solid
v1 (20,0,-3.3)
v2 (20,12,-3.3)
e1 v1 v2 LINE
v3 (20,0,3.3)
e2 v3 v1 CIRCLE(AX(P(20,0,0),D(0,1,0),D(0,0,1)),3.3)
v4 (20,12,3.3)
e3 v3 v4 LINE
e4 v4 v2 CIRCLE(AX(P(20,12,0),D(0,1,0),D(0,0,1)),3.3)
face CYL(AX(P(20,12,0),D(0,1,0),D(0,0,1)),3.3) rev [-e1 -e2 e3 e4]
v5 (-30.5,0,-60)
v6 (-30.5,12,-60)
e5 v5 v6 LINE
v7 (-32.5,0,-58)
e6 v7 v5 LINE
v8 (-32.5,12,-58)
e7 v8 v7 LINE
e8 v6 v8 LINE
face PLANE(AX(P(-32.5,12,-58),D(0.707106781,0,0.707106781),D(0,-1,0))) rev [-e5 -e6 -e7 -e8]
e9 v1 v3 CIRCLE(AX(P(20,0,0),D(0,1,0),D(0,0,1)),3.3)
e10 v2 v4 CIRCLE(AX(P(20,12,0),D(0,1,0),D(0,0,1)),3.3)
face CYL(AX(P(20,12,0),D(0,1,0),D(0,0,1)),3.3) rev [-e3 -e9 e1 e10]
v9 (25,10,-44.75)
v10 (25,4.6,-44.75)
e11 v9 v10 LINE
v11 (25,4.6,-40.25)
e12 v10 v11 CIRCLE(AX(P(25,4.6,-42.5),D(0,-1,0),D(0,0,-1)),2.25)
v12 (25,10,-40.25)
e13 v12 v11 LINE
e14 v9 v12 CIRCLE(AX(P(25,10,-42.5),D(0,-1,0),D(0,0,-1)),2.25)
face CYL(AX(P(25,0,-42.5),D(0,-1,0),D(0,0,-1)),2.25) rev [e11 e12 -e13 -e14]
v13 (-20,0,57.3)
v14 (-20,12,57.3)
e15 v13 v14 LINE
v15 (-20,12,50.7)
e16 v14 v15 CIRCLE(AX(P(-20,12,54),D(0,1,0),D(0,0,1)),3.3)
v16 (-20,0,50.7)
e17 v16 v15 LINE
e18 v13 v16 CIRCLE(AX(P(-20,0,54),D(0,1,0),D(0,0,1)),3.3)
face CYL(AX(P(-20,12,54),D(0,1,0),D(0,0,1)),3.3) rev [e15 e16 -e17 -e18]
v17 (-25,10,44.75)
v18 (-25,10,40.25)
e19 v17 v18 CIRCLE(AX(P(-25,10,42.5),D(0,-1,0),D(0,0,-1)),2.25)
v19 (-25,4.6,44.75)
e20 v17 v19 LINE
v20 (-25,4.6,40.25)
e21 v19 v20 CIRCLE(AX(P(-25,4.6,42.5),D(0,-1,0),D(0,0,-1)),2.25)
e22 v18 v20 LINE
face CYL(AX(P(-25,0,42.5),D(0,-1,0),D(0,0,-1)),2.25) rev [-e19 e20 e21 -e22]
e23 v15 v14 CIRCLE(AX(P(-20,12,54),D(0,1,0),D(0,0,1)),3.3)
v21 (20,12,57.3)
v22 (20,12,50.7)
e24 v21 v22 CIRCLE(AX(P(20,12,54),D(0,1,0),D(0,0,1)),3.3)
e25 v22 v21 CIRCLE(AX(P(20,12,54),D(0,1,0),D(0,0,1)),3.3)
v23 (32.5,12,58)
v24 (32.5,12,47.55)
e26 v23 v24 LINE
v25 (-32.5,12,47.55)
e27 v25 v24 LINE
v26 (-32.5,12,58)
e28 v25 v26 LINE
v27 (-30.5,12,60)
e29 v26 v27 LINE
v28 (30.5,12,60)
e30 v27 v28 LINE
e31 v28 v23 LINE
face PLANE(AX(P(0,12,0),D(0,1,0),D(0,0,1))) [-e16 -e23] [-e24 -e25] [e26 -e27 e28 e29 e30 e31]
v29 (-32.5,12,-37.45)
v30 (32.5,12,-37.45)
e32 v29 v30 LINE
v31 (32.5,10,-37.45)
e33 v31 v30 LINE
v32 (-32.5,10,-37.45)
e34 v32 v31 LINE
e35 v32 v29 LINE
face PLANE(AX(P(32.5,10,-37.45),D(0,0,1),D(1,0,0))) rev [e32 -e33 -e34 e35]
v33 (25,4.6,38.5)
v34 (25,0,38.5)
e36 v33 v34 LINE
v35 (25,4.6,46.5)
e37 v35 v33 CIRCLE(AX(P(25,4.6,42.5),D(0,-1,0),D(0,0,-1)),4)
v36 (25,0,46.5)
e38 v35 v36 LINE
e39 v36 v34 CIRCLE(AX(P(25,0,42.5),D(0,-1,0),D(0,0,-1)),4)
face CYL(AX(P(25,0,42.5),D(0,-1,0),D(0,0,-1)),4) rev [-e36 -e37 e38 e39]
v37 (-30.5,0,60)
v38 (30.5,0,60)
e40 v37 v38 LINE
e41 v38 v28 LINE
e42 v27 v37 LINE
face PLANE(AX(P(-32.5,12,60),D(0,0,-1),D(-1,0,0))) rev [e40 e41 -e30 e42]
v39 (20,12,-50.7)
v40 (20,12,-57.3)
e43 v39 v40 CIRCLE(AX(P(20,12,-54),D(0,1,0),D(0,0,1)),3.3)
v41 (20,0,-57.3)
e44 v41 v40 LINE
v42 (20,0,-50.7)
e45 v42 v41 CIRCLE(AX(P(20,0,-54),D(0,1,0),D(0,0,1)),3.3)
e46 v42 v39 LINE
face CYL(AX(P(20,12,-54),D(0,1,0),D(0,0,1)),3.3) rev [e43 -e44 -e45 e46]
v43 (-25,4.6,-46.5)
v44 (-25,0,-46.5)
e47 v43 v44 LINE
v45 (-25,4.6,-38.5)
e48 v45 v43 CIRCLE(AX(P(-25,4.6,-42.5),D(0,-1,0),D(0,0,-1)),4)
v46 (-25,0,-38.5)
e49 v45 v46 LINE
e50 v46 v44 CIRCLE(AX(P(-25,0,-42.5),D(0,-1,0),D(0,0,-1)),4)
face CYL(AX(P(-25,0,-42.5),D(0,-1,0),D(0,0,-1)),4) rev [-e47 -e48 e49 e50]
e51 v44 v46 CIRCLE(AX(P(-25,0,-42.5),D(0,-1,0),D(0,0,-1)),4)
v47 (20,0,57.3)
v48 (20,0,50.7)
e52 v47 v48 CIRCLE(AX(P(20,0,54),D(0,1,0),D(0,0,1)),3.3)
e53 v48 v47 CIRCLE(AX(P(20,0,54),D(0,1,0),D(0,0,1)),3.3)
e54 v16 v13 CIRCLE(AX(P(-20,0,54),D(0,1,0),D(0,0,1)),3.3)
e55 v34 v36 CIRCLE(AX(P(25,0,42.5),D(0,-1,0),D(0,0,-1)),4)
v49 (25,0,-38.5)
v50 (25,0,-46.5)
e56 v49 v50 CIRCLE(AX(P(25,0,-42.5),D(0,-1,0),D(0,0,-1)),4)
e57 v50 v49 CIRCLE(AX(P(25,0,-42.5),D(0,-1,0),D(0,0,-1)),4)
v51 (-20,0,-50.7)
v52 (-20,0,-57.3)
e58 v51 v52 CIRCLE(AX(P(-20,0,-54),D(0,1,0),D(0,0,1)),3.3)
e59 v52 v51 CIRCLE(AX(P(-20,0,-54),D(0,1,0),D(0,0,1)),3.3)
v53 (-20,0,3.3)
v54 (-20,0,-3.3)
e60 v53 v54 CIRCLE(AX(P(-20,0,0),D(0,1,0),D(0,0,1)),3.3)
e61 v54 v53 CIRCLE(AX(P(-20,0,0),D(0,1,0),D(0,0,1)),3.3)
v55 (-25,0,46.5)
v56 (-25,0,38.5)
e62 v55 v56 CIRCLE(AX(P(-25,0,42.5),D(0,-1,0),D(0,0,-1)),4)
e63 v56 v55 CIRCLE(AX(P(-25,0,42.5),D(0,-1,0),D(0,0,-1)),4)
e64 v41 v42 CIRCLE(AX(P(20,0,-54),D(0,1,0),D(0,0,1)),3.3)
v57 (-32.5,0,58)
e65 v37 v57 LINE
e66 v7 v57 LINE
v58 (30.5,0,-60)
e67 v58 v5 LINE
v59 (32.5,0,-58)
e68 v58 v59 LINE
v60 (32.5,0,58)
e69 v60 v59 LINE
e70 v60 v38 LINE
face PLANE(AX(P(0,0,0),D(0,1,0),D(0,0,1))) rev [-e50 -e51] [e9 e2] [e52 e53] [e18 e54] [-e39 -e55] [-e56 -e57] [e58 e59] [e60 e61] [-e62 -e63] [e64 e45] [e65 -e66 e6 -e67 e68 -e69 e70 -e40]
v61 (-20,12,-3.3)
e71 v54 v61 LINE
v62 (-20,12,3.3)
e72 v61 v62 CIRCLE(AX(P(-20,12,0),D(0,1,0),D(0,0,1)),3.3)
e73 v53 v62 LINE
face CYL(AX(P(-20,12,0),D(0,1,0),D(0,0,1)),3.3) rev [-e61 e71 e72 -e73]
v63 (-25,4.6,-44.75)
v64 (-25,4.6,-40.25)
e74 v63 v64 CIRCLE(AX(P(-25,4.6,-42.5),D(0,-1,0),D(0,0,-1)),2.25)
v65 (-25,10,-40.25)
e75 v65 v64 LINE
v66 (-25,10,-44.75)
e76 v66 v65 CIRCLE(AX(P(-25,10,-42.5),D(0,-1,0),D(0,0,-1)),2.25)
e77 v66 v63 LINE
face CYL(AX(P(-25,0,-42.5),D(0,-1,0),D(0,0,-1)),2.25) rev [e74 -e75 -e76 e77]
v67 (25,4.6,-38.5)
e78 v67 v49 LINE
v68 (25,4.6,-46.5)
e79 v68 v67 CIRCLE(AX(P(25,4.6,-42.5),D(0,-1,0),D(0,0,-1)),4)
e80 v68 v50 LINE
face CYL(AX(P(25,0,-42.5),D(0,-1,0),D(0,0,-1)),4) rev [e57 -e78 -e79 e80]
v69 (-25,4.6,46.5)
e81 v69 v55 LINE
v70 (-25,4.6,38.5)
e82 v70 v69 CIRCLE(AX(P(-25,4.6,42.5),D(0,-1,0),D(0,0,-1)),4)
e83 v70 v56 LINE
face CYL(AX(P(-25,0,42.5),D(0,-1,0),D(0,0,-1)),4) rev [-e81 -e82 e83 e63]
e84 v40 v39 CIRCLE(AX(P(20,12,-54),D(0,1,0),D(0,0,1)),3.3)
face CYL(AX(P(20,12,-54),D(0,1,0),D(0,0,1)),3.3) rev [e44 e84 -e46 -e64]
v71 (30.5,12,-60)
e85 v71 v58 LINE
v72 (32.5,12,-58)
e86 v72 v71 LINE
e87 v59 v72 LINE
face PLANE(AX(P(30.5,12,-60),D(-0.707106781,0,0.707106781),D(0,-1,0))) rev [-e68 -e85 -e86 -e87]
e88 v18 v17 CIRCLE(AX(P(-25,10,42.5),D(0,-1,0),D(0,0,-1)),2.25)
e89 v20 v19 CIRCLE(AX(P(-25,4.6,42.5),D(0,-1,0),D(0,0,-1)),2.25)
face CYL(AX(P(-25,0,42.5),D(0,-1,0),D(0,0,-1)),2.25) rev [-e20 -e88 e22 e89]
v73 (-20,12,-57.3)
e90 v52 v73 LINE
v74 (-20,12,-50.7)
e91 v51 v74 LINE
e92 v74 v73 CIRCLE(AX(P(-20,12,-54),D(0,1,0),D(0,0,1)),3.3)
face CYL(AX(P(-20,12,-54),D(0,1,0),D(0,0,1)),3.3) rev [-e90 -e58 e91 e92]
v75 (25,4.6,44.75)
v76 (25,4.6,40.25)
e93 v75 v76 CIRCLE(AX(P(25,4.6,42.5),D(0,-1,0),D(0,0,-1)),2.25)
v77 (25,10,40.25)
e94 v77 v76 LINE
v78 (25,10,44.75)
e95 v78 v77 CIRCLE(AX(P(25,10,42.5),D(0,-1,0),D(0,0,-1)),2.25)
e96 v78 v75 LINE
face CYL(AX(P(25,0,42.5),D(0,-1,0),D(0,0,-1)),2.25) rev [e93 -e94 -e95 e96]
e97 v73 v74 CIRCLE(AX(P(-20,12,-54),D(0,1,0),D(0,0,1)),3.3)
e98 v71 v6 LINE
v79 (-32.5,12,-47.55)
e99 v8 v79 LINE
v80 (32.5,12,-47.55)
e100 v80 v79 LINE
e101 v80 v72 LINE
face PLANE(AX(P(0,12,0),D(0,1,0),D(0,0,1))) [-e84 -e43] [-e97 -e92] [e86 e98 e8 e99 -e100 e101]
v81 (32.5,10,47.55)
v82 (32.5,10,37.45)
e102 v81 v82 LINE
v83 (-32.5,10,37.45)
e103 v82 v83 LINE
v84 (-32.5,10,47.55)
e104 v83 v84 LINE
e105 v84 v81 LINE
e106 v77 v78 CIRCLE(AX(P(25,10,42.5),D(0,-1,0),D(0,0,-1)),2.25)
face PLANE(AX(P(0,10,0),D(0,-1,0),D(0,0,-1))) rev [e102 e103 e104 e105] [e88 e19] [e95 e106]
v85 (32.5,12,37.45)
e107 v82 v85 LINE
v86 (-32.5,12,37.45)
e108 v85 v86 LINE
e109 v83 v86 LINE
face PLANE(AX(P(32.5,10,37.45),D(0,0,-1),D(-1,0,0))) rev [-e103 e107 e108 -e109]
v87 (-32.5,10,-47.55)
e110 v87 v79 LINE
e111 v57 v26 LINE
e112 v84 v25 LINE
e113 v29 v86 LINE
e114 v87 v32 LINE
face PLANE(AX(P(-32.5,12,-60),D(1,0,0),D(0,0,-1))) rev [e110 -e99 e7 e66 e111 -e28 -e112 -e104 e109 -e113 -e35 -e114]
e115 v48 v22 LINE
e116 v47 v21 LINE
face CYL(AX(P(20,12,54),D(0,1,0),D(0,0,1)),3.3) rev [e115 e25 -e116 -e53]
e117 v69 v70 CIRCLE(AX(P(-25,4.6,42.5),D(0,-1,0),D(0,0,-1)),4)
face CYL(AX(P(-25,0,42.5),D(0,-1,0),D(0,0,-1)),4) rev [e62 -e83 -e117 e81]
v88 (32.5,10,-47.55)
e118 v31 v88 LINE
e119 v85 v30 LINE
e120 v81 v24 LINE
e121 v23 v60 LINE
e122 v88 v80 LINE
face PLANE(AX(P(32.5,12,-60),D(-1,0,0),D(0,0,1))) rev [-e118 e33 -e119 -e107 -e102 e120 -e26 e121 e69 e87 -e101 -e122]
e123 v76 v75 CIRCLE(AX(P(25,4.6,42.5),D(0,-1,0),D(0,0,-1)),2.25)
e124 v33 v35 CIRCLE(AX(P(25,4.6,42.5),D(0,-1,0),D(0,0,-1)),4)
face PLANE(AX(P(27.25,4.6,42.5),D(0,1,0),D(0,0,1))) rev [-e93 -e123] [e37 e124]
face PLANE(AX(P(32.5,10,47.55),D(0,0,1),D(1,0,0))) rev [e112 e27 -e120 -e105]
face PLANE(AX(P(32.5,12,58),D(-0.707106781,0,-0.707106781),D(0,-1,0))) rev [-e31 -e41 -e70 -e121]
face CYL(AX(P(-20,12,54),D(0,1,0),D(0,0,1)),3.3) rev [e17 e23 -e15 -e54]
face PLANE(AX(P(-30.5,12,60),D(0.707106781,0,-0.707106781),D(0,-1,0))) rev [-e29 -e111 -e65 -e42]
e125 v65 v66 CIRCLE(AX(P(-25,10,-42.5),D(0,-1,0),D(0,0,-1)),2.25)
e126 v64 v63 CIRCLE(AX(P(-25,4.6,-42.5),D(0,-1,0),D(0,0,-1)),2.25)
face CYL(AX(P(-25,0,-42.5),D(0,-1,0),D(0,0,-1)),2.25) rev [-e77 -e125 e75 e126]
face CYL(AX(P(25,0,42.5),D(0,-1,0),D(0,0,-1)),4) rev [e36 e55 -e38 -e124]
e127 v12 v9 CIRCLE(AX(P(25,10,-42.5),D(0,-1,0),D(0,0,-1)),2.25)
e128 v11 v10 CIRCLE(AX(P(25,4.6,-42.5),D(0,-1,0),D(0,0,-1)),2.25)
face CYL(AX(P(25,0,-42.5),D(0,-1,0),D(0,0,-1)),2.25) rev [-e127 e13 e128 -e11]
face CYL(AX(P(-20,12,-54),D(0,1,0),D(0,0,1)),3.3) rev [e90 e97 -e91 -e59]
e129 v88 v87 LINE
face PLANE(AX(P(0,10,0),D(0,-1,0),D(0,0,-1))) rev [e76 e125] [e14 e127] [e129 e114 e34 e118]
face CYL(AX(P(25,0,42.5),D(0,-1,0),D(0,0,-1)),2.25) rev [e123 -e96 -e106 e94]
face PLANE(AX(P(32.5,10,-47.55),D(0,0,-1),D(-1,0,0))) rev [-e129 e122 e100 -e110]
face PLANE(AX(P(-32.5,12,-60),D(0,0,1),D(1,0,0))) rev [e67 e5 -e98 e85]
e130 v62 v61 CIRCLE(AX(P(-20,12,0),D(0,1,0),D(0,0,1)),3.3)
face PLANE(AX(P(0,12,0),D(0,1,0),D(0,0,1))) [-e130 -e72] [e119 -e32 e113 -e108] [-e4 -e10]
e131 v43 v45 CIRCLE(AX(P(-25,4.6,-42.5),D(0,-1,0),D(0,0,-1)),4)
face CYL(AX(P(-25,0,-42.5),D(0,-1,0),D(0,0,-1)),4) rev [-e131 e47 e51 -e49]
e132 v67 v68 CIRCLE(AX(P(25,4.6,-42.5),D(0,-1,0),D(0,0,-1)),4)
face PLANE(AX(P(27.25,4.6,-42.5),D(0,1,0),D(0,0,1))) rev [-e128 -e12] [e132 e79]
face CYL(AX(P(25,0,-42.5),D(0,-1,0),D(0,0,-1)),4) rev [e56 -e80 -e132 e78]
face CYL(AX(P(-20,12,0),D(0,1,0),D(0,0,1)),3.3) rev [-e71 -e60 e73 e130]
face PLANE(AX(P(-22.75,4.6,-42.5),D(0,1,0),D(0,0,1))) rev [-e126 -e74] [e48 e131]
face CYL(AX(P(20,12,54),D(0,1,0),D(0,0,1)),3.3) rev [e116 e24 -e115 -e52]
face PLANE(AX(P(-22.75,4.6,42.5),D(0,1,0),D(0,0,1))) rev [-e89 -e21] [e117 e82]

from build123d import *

# Parameters (mm, degrees)
SKETCH_1_W                   = 65
SKETCH_1_H                   = 120
EXTRUDE_1_DEPTH              = 12
HOLE_WIZARD_M6_1_D           = 6.6
SKETCH_4_W                   = 65
SKETCH_4_H                   = 10.1
CUT_EXTRUDE_1_DEPTH          = 2
CHAMFER_1_SIZE               = 2
HOLE_WIZARD_M4_1_D           = 4.5
HOLE_WIZARD_M4_1_CBORE_D     = 8
HOLE_WIZARD_M4_1_CBORE_DEPTH = 4.6


with BuildPart() as part:
    # 草图1 → 凸台-拉伸1 (new body)
    with BuildSketch(Plane(origin=(0, 0, 0), x_dir=(1, 0, 0), z_dir=(0, 1, 0))):
        Rectangle(SKETCH_1_W, SKETCH_1_H)
    extrude(amount=EXTRUDE_1_DEPTH)

    # M6 间隙孔1 (through all)
    with Locations(Plane(origin=(0, 12, 0), x_dir=(1, 0, 0), z_dir=(0, 1, 0))):
        with Locations((-20, -54), (20, -54), (-20, 0), (20, 0), (-20, 54), (20, 54)):
            Hole(HOLE_WIZARD_M6_1_D / 2)

    # 草图4 → 切除-拉伸1 (cut)
    with BuildSketch(Plane(origin=(0, 12, 0), x_dir=(1, 0, 0), z_dir=(0, 1, 0))):
        with Locations((0, 42.5)):
            Rectangle(SKETCH_4_W, SKETCH_4_H)
        with Locations((0, -42.5)):
            Rectangle(SKETCH_4_W, SKETCH_4_H)
    extrude(amount=-CUT_EXTRUDE_1_DEPTH, mode=Mode.SUBTRACT)

    # 倒角1
    chamfer_1_edges = [part.edges().sort_by_distance(p)[0] for p in [
        (32.5, 6, 60),
        (-32.5, 6, 60),
        (-32.5, 6, -60),
        (32.5, 6, -60),
    ]]
    chamfer(chamfer_1_edges, length=CHAMFER_1_SIZE)

    # M4 六角圆柱头螺钉的柱形沉头孔1 (through all)
    with Locations(Plane(origin=(0, 0, 0), x_dir=(-1, 0, 0), z_dir=(0, -1, 0))):
        with Locations((-25, 42.5), (-25, -42.5), (25, -42.5), (25, 42.5)):
            CounterBoreHole(HOLE_WIZARD_M4_1_D / 2, HOLE_WIZARD_M4_1_CBORE_D / 2, HOLE_WIZARD_M4_1_CBORE_DEPTH)


solid = part.part
